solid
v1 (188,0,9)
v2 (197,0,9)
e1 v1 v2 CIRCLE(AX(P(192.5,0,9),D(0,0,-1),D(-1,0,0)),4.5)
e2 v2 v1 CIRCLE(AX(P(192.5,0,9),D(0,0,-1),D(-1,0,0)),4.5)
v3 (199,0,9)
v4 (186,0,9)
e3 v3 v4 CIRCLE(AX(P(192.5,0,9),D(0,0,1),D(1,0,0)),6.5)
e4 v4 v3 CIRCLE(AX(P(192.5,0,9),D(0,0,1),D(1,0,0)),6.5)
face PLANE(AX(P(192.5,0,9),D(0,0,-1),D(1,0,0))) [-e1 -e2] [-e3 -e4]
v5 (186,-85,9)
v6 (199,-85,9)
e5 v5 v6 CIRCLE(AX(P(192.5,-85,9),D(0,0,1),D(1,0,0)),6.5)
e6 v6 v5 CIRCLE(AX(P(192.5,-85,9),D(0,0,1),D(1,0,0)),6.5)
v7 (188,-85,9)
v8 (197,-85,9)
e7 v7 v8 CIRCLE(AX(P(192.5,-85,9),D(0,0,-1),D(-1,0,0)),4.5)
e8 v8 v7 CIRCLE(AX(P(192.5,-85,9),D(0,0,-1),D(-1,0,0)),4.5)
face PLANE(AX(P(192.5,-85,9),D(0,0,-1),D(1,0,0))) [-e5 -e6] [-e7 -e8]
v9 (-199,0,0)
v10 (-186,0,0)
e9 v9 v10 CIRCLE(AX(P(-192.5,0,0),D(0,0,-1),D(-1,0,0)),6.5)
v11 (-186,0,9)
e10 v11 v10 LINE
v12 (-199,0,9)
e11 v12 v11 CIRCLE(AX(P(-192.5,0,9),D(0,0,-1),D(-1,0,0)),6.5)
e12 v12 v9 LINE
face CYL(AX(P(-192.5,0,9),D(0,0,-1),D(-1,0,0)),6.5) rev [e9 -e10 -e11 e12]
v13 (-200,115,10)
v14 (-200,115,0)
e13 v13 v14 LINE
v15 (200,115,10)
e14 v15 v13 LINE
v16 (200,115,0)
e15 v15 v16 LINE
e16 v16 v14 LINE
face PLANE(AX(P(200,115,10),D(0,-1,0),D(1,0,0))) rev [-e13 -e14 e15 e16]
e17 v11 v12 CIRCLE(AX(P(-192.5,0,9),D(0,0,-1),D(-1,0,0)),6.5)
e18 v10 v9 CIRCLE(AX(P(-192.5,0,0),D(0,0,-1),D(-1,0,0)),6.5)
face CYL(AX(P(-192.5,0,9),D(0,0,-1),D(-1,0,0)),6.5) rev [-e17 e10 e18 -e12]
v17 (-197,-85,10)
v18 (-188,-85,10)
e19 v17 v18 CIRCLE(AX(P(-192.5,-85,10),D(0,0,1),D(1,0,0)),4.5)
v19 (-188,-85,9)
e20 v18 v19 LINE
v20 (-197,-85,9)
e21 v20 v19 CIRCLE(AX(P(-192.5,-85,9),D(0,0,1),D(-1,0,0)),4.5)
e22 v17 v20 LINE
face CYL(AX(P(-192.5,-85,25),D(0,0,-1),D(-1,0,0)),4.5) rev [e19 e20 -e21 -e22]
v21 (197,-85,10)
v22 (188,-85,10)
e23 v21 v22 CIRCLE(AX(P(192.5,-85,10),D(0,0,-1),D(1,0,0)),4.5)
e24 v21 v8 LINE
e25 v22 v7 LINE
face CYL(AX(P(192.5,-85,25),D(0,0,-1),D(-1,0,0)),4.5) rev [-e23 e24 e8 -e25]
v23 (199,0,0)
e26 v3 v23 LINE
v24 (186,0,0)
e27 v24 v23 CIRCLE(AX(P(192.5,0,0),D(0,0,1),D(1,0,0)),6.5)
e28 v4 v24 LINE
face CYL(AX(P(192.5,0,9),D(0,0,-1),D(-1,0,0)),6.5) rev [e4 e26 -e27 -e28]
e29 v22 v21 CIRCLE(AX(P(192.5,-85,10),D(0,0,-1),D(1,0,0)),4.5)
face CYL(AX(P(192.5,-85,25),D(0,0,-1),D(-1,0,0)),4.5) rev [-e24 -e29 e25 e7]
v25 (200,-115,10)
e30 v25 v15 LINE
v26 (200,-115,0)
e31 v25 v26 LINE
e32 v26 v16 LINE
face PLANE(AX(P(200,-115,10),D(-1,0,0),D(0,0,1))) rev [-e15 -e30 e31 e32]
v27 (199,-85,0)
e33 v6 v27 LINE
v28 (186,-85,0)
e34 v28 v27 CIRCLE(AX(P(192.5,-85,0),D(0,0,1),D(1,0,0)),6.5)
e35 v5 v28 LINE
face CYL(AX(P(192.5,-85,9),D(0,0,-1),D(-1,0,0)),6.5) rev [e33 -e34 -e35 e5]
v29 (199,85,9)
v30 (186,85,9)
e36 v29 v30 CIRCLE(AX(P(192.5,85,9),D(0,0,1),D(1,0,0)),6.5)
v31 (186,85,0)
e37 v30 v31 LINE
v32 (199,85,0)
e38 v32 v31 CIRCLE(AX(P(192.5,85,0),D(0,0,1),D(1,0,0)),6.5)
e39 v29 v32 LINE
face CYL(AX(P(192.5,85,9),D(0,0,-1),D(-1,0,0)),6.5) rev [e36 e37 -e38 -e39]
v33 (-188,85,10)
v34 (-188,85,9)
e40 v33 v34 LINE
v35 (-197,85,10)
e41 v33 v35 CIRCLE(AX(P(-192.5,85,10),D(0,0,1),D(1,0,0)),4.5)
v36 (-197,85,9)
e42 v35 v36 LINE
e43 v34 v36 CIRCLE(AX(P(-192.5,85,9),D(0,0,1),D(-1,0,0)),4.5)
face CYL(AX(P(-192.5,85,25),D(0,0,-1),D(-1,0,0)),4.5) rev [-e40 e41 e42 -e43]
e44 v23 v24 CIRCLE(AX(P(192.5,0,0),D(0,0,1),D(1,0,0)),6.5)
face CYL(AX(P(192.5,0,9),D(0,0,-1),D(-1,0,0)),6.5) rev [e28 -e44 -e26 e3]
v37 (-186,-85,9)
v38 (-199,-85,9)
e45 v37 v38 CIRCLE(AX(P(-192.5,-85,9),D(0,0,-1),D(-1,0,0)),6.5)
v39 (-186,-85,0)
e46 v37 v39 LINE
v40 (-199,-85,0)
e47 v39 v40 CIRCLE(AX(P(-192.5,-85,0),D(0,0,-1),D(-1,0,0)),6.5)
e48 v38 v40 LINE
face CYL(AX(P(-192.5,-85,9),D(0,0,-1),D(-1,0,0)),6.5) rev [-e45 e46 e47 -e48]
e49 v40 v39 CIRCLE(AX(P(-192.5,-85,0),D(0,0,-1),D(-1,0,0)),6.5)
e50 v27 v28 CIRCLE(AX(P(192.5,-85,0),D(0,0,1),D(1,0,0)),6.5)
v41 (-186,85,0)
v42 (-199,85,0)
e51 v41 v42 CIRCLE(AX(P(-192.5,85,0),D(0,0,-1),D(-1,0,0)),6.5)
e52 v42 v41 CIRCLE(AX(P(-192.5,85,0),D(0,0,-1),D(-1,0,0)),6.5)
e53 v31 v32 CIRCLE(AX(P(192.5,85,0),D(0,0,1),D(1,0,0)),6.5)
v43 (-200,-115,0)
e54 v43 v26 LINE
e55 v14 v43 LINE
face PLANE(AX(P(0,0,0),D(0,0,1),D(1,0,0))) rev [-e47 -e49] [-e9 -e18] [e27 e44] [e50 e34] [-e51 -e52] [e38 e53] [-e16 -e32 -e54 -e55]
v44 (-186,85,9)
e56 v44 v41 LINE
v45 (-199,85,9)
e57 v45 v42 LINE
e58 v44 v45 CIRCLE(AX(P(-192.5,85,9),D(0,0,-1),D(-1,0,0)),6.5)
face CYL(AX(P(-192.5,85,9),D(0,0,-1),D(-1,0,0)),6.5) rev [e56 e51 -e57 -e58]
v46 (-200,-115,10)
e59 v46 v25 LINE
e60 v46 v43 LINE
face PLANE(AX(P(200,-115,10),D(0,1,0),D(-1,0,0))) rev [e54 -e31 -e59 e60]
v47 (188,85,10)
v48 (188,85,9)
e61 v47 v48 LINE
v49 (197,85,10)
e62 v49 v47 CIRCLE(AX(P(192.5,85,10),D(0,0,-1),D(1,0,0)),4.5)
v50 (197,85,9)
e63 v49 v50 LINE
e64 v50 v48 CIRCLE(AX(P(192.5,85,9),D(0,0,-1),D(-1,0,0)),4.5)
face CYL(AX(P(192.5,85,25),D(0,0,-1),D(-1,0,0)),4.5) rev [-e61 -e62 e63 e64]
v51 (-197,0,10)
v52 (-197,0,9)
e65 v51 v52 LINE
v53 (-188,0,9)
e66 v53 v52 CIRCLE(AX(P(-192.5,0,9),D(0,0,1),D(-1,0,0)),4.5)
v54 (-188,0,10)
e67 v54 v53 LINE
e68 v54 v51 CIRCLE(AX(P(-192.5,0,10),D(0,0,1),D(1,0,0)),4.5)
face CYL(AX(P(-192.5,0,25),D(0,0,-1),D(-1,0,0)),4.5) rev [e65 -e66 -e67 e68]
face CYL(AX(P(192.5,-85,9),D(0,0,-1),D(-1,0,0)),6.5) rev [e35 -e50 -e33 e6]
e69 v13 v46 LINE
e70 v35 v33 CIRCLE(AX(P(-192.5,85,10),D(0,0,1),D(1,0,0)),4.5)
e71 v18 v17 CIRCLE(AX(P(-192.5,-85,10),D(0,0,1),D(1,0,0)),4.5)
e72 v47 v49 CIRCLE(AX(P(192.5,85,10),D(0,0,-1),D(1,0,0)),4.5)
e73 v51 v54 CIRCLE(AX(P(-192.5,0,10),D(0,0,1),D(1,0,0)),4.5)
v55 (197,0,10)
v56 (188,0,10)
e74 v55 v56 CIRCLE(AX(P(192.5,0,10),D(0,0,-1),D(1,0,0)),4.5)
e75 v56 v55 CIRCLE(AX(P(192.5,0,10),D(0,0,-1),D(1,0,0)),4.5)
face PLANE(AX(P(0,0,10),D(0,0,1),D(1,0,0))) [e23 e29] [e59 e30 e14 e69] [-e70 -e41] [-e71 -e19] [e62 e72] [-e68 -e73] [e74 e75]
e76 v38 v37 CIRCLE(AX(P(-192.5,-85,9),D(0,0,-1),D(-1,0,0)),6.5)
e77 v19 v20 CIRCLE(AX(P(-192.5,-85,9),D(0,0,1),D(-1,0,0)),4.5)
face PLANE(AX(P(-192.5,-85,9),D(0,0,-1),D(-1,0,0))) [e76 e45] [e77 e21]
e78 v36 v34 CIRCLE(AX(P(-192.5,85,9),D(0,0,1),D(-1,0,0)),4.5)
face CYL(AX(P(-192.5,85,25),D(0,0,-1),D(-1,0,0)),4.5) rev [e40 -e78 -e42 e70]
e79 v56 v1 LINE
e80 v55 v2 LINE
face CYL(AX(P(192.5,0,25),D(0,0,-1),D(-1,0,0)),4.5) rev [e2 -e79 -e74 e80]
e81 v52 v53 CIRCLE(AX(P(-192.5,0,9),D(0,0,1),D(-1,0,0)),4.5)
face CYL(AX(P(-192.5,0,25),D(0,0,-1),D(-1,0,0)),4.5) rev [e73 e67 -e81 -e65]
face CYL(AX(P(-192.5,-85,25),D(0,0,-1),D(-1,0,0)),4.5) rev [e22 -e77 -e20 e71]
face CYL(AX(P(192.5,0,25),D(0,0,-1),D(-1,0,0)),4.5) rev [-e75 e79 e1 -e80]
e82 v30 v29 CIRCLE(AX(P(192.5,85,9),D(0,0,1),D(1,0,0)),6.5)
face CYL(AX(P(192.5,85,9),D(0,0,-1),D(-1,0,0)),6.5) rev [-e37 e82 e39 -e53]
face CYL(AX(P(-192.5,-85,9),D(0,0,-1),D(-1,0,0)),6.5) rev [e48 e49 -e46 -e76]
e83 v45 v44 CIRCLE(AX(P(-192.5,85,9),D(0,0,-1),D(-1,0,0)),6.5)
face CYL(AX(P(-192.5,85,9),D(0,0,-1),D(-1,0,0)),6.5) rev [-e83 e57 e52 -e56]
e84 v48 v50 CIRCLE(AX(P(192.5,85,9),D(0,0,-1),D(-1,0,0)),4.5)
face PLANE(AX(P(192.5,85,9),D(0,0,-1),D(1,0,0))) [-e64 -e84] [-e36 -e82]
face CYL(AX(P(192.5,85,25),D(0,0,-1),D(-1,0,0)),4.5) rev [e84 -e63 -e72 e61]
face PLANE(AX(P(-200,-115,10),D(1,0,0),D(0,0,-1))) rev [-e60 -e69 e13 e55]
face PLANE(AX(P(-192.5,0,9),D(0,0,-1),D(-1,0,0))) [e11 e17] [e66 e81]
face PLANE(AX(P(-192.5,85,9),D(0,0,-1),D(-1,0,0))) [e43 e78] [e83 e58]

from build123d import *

# Parameters (mm, degrees)
SKETCH1_W           = 400
SKETCH1_H           = 230
BOSS_EXTRUDE1_DEPTH = 10
SKETCH2_R           = 4.5
CUT_EXTRUDE1_DEPTH  = 25
SKETCH3_R           = 6.5
CUT_EXTRUDE2_DEPTH  = 9


with BuildPart() as part:
    # Sketch1 → Boss-Extrude1 (new body)
    with BuildSketch(Plane.XY):
        Rectangle(SKETCH1_W, SKETCH1_H)
    extrude(amount=BOSS_EXTRUDE1_DEPTH)

    # Sketch2 → Cut-Extrude1 (cut)
    with BuildSketch(Plane(origin=(0, 0, 0), x_dir=(-1, 0, 0), z_dir=(0, 0, -1))):
        with Locations((192.5, -85)):
            Circle(SKETCH2_R)
        with Locations((192.5, 0)):
            Circle(SKETCH2_R)
        with Locations((192.5, 85)):
            Circle(SKETCH2_R)
    cut_extrude1 = extrude(amount=-CUT_EXTRUDE1_DEPTH, mode=Mode.SUBTRACT)

    # Sketch3 → Cut-Extrude2 (cut)
    with BuildSketch(Plane(origin=(0, 0, 0), x_dir=(-1, 0, 0), z_dir=(0, 0, -1))):
        with Locations((192.5, -85)):
            Circle(SKETCH3_R)
        with Locations((192.5, 0)):
            Circle(SKETCH3_R)
        with Locations((192.5, 85)):
            Circle(SKETCH3_R)
    cut_extrude2 = extrude(amount=-CUT_EXTRUDE2_DEPTH, mode=Mode.SUBTRACT)

    # Mirror1: Cut-Extrude1, Cut-Extrude2 across plane
    add(cut_extrude1.mirror(Plane(origin=(0, 0, 0), x_dir=(0, 0, 1), z_dir=(1, 0, 0))), mode=Mode.SUBTRACT)
    add(cut_extrude2.mirror(Plane(origin=(0, 0, 0), x_dir=(0, 0, 1), z_dir=(1, 0, 0))), mode=Mode.SUBTRACT)


solid = part.part
